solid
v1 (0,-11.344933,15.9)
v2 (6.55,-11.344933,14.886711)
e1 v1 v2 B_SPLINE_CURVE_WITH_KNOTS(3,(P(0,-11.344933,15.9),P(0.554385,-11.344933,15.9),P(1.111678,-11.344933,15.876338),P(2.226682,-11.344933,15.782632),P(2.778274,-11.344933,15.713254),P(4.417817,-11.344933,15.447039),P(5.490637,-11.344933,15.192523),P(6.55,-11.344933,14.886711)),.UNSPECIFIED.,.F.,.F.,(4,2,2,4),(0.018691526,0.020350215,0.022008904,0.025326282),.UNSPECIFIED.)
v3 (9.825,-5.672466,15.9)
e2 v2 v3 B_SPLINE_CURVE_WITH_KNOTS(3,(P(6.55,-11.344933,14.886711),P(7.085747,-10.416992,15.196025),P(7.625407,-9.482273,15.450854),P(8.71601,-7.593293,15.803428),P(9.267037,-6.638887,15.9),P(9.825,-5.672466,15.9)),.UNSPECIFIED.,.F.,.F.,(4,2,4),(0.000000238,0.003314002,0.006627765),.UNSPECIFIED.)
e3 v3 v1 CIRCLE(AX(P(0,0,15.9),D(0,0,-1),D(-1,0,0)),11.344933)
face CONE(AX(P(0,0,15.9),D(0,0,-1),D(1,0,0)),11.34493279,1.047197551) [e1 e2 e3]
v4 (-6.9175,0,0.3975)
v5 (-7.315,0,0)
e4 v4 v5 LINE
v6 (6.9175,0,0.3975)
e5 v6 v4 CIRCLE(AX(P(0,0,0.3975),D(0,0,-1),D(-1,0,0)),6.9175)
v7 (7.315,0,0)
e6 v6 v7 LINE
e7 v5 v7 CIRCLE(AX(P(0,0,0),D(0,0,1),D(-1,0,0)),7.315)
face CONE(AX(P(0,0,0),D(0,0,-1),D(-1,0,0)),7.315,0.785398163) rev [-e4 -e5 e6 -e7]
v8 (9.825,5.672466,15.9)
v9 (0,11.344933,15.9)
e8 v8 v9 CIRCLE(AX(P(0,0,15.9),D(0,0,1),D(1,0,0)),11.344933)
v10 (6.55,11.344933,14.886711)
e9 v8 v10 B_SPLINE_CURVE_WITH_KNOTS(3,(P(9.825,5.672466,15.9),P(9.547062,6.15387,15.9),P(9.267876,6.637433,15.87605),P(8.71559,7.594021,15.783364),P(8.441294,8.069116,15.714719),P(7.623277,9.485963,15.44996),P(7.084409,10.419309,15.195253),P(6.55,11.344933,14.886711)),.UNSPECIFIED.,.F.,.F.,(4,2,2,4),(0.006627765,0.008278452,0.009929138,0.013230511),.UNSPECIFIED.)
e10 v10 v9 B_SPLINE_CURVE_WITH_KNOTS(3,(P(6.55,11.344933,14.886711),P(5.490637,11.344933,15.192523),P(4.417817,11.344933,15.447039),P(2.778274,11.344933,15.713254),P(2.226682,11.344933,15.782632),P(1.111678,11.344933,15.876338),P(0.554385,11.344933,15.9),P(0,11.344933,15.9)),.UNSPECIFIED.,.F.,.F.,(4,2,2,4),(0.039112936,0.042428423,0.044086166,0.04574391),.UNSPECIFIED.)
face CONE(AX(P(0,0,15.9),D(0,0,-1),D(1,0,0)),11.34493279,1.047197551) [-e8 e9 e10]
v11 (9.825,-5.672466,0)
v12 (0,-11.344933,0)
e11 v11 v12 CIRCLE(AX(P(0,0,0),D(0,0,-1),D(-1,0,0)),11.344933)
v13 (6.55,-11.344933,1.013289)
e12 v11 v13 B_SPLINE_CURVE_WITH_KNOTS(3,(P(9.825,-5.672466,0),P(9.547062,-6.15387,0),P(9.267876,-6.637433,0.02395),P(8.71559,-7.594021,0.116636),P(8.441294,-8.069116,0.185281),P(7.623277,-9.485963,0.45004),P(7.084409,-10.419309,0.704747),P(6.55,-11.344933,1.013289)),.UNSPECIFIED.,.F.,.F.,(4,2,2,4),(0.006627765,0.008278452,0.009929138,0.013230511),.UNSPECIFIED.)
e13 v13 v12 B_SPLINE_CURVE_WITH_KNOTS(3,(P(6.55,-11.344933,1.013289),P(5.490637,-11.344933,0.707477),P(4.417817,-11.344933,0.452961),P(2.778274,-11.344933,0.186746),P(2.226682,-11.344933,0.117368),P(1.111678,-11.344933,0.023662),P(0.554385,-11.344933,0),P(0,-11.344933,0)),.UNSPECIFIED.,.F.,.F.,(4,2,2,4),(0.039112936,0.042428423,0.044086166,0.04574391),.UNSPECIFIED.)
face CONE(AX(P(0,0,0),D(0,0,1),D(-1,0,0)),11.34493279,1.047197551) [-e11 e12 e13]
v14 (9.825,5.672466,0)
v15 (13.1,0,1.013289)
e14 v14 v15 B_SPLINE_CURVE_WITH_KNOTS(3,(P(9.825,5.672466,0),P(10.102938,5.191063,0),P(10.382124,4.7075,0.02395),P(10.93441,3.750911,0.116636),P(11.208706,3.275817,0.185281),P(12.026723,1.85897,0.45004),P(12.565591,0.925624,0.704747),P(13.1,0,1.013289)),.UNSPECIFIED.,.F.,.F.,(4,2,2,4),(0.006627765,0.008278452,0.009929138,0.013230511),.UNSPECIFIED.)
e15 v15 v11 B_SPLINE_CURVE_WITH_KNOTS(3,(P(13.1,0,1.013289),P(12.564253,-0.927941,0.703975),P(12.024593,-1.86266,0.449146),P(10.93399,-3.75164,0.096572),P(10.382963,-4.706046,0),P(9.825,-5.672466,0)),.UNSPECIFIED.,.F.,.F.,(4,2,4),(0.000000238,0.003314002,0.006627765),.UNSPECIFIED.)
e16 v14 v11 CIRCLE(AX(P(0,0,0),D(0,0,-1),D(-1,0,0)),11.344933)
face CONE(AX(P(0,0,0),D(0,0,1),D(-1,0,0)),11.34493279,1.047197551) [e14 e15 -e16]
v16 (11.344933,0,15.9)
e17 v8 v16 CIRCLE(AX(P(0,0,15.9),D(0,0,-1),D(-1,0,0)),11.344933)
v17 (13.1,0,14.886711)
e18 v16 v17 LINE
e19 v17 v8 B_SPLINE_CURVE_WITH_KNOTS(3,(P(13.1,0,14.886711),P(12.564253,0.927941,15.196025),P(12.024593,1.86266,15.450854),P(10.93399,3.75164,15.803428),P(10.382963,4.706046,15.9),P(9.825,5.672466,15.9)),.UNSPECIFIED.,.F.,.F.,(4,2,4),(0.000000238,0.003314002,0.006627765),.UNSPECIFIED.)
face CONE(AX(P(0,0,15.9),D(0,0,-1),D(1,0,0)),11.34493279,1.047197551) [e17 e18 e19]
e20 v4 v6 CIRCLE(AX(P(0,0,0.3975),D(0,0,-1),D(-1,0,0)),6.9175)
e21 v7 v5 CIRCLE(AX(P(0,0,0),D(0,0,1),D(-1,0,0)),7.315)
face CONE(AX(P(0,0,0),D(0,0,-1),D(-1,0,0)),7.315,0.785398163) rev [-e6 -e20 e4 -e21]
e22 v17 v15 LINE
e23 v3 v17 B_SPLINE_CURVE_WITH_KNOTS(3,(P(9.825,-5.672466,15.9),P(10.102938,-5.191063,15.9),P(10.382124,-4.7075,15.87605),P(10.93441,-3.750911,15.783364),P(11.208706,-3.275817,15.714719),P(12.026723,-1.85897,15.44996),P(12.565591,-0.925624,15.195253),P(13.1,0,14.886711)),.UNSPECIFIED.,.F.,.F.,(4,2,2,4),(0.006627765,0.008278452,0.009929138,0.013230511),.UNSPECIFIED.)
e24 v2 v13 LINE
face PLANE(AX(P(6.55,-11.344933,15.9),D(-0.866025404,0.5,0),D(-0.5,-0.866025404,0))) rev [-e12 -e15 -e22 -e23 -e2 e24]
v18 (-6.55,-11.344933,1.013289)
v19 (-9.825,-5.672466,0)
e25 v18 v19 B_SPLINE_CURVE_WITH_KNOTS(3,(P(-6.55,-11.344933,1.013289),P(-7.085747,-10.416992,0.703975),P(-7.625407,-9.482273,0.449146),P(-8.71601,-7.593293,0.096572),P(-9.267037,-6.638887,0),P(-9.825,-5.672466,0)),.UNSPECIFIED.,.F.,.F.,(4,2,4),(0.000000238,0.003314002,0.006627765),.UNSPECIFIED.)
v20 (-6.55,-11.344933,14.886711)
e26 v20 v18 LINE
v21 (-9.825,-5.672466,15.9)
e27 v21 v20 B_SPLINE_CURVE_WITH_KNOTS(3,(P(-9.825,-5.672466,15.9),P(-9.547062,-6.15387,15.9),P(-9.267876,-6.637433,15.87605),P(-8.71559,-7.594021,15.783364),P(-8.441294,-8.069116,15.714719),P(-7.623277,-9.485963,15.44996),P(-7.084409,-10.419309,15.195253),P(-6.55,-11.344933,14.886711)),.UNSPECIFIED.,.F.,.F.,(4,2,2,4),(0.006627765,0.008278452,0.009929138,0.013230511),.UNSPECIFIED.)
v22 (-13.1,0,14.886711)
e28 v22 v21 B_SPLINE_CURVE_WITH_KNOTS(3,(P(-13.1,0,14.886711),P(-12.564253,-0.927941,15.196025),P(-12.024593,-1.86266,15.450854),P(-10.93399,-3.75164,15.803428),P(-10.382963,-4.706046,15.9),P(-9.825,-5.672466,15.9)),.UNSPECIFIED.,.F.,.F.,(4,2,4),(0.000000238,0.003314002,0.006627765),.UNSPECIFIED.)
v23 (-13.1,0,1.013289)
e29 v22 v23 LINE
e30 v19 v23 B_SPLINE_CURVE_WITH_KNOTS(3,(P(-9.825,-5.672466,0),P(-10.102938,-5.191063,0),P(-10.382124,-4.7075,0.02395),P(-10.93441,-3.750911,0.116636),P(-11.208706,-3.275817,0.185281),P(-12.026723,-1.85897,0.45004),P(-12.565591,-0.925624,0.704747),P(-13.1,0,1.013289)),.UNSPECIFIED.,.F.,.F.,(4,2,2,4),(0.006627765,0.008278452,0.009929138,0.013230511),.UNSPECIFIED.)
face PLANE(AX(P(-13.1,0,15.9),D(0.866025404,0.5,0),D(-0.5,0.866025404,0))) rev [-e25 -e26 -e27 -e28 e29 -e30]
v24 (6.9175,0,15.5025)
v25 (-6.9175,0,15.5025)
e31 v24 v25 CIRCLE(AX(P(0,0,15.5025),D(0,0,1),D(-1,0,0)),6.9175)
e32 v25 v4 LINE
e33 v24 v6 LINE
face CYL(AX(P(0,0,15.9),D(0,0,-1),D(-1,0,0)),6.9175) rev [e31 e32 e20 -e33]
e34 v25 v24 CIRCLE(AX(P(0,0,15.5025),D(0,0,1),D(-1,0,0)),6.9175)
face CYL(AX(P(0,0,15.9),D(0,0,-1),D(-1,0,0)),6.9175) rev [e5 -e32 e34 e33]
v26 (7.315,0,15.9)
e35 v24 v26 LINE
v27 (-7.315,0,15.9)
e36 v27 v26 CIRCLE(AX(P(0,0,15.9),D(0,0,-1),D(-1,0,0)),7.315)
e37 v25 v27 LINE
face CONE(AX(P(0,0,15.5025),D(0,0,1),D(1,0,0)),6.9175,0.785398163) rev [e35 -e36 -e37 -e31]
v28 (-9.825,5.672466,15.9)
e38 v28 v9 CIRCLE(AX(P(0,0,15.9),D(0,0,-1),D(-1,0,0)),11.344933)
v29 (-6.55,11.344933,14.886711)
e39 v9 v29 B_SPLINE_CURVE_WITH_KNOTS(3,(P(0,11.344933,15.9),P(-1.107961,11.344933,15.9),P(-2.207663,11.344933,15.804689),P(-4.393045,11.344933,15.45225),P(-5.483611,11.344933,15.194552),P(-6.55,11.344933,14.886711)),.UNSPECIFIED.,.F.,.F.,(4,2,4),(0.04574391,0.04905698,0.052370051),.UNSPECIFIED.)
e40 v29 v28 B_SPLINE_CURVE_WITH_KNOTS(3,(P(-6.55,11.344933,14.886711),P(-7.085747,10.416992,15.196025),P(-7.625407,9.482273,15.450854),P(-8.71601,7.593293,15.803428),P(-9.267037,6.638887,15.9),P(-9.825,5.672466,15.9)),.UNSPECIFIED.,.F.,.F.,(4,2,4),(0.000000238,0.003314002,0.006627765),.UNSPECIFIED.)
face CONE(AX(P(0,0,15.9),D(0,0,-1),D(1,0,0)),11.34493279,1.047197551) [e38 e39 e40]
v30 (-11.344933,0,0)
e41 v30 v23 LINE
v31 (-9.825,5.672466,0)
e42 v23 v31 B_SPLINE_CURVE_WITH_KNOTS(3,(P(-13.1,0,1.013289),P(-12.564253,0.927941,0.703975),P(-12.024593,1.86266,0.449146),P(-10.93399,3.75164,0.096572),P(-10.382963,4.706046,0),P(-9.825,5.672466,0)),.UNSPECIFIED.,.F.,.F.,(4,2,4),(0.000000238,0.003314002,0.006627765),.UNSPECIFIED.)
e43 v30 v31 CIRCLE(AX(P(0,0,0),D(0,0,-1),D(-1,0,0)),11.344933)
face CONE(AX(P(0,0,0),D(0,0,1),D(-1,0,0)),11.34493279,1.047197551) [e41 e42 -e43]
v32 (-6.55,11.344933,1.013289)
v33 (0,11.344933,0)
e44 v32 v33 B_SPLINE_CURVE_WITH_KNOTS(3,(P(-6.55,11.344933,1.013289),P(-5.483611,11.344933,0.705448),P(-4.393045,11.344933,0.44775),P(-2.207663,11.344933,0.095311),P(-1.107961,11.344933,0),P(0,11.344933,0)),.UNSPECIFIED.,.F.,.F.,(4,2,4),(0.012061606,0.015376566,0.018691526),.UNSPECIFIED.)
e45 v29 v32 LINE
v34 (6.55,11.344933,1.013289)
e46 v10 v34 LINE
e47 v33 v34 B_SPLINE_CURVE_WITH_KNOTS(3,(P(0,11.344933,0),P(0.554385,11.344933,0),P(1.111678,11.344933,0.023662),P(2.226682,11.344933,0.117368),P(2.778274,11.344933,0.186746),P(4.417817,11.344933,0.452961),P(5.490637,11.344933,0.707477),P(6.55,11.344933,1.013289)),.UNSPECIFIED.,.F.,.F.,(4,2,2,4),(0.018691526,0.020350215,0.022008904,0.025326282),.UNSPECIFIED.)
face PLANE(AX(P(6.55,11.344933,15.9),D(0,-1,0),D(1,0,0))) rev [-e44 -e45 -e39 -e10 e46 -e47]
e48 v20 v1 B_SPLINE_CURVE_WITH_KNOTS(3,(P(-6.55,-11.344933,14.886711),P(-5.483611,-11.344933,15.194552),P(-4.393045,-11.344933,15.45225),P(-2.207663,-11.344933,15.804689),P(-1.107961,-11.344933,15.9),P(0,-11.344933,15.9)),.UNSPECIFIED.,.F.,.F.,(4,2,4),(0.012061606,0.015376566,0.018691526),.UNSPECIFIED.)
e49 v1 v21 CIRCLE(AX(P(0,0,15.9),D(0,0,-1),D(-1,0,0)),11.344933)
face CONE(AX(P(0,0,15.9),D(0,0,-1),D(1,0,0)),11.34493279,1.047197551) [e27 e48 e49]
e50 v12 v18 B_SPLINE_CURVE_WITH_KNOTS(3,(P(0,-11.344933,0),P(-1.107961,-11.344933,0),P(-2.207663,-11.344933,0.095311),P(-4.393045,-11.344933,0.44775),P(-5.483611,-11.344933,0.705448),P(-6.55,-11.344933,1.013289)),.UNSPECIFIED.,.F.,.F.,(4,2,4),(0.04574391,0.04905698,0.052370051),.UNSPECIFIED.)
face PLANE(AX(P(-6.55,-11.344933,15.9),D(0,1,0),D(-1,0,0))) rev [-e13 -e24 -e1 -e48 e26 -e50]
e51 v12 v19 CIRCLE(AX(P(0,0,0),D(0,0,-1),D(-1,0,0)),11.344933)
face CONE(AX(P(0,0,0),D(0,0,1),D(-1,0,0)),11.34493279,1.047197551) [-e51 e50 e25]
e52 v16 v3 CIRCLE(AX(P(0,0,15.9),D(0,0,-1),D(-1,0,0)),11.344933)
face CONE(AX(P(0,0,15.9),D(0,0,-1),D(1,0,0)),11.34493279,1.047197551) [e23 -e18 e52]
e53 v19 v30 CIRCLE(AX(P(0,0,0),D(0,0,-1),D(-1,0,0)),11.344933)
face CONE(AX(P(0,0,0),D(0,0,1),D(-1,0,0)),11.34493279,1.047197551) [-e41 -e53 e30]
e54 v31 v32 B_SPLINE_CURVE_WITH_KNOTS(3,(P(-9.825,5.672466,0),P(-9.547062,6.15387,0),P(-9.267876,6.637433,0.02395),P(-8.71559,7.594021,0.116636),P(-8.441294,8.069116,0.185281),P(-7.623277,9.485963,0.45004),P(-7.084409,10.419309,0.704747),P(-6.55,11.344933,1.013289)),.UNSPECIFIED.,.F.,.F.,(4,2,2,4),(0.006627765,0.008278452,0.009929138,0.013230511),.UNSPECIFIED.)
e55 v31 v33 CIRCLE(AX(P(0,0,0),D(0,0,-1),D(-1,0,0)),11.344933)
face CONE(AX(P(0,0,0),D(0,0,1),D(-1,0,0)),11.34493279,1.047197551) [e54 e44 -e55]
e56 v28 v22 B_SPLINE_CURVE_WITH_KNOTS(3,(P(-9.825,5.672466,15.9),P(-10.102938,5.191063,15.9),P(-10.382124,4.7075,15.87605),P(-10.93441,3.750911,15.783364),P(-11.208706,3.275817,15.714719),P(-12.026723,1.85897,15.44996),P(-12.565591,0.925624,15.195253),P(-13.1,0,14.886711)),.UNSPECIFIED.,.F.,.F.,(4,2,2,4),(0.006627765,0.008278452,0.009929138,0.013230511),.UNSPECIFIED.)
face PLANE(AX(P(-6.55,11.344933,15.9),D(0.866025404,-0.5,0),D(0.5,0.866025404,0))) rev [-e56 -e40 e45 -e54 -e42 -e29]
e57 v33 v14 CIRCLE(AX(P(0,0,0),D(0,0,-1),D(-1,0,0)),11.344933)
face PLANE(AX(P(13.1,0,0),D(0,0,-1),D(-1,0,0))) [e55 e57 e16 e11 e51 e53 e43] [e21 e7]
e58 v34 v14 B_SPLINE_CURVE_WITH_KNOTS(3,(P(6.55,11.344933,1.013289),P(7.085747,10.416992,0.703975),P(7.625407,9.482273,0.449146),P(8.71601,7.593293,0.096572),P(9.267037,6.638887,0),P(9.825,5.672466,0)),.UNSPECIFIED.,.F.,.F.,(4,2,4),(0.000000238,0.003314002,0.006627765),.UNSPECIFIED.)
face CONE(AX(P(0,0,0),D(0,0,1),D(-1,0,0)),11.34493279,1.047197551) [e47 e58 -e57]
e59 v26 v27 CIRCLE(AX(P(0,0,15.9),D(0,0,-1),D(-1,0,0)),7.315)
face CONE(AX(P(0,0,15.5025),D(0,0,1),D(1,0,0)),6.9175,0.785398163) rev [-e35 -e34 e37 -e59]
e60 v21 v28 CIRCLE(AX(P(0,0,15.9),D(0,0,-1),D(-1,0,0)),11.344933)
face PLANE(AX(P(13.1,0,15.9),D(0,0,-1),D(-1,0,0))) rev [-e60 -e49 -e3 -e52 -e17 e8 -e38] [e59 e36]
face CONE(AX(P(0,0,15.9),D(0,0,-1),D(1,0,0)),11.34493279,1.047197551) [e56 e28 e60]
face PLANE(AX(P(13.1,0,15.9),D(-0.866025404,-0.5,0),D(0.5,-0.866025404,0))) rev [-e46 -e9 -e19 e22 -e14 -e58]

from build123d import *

# Parameters (mm, degrees)
SKETCH1_R          = 6.9175
BOSS_EXTRUDE_DEPTH = 15.9
SKETCH2_OUTSIDE_W  = 120.762
SKETCH2_OUTSIDE_H  = 117.252
SKETCH2_OUTSIDE_R  = 11.34493279
CUT_EXTRUDE1_DEPTH = 24.518662802
CUT_EXTRUDE1_DRAFT = -60
SKETCH3_OUTSIDE_W  = 120.762
SKETCH3_OUTSIDE_H  = 117.252
SKETCH3_OUTSIDE_R  = 11.34493279
CUT_EXTRUDE2_DEPTH = 24.518662802
CUT_EXTRUDE2_DRAFT = -60
CHAMFER1_SIZE      = 0.3975


with BuildPart() as part:
    # Sketch1 → Boss-Extrude (new body)
    with BuildSketch(Plane.XY):
        Polygon((6.55, 11.34493279), (-6.55, 11.34493279), (-13.1, 0), (-6.55, -11.34493279), (6.55, -11.34493279), (13.1, 0), align=None)
        Circle(SKETCH1_R, mode=Mode.SUBTRACT)
    extrude(amount=BOSS_EXTRUDE_DEPTH)


with BuildPart() as cut_extrude1_tool:
    # Sketch2 outside → Cut-Extrude1 (with draft: the straight prism first)
    with BuildSketch(Plane(origin=(0, 0, 0), x_dir=(-1, 0, 0), z_dir=(0, 0, -1))):
        Rectangle(SKETCH2_OUTSIDE_W, SKETCH2_OUTSIDE_H)
        Circle(SKETCH2_OUTSIDE_R, mode=Mode.SUBTRACT)
    extrude(amount=-CUT_EXTRUDE1_DEPTH)
    # Cut-Extrude1: the draft: its side faces are tilted about the plane it starts from
    cut_extrude1_sides = [cut_extrude1_tool.faces().sort_by_distance(p)[0] for p in [
        (0, -58.626, 12.259331401),
        (-60.381, 0, 12.259331401),
        (0, 58.626, 12.259331401),
        (60.381, 0, 12.259331401),
        (11.34493279, 0, 12.259331401),
    ]]
    draft(cut_extrude1_sides, Plane(origin=(0, 0, 0), x_dir=(-1, 0, 0), z_dir=(0, 0, -1)), CUT_EXTRUDE1_DRAFT)


with BuildPart() as part_1:
    add(part.part)

    # Cut-Extrude1: cut by cut_extrude1_tool
    add(cut_extrude1_tool.part, mode=Mode.SUBTRACT)


with BuildPart() as cut_extrude2_tool:
    # Sketch3 outside → Cut-Extrude2 (with draft: the straight prism first)
    with BuildSketch(Plane.XY.offset(15.9)):
        Rectangle(SKETCH3_OUTSIDE_W, SKETCH3_OUTSIDE_H)
        Circle(SKETCH3_OUTSIDE_R, mode=Mode.SUBTRACT)
    extrude(amount=-CUT_EXTRUDE2_DEPTH)
    # Cut-Extrude2: the draft: its side faces are tilted about the plane it starts from
    cut_extrude2_sides = [cut_extrude2_tool.faces().sort_by_distance(p)[0] for p in [
        (0, -58.626, 3.640668599),
        (60.381, 0, 3.640668599),
        (0, 58.626, 3.640668599),
        (-60.381, 0, 3.640668599),
        (-11.34493279, 0, 3.640668599),
    ]]
    draft(cut_extrude2_sides, Plane.XY.offset(15.9), CUT_EXTRUDE2_DRAFT)


with BuildPart() as part_2:
    add(part_1.part)

    # Cut-Extrude2: cut by cut_extrude2_tool
    add(cut_extrude2_tool.part, mode=Mode.SUBTRACT)

    # Chamfer1
    chamfer1_edges = [part_2.edges().sort_by_distance(p)[0] for p in [
        (-6.9175, 0, 0),
        (-6.9175, 0, 15.9),
    ]]
    chamfer(chamfer1_edges, length=CHAMFER1_SIZE)


solid = part_2.part
